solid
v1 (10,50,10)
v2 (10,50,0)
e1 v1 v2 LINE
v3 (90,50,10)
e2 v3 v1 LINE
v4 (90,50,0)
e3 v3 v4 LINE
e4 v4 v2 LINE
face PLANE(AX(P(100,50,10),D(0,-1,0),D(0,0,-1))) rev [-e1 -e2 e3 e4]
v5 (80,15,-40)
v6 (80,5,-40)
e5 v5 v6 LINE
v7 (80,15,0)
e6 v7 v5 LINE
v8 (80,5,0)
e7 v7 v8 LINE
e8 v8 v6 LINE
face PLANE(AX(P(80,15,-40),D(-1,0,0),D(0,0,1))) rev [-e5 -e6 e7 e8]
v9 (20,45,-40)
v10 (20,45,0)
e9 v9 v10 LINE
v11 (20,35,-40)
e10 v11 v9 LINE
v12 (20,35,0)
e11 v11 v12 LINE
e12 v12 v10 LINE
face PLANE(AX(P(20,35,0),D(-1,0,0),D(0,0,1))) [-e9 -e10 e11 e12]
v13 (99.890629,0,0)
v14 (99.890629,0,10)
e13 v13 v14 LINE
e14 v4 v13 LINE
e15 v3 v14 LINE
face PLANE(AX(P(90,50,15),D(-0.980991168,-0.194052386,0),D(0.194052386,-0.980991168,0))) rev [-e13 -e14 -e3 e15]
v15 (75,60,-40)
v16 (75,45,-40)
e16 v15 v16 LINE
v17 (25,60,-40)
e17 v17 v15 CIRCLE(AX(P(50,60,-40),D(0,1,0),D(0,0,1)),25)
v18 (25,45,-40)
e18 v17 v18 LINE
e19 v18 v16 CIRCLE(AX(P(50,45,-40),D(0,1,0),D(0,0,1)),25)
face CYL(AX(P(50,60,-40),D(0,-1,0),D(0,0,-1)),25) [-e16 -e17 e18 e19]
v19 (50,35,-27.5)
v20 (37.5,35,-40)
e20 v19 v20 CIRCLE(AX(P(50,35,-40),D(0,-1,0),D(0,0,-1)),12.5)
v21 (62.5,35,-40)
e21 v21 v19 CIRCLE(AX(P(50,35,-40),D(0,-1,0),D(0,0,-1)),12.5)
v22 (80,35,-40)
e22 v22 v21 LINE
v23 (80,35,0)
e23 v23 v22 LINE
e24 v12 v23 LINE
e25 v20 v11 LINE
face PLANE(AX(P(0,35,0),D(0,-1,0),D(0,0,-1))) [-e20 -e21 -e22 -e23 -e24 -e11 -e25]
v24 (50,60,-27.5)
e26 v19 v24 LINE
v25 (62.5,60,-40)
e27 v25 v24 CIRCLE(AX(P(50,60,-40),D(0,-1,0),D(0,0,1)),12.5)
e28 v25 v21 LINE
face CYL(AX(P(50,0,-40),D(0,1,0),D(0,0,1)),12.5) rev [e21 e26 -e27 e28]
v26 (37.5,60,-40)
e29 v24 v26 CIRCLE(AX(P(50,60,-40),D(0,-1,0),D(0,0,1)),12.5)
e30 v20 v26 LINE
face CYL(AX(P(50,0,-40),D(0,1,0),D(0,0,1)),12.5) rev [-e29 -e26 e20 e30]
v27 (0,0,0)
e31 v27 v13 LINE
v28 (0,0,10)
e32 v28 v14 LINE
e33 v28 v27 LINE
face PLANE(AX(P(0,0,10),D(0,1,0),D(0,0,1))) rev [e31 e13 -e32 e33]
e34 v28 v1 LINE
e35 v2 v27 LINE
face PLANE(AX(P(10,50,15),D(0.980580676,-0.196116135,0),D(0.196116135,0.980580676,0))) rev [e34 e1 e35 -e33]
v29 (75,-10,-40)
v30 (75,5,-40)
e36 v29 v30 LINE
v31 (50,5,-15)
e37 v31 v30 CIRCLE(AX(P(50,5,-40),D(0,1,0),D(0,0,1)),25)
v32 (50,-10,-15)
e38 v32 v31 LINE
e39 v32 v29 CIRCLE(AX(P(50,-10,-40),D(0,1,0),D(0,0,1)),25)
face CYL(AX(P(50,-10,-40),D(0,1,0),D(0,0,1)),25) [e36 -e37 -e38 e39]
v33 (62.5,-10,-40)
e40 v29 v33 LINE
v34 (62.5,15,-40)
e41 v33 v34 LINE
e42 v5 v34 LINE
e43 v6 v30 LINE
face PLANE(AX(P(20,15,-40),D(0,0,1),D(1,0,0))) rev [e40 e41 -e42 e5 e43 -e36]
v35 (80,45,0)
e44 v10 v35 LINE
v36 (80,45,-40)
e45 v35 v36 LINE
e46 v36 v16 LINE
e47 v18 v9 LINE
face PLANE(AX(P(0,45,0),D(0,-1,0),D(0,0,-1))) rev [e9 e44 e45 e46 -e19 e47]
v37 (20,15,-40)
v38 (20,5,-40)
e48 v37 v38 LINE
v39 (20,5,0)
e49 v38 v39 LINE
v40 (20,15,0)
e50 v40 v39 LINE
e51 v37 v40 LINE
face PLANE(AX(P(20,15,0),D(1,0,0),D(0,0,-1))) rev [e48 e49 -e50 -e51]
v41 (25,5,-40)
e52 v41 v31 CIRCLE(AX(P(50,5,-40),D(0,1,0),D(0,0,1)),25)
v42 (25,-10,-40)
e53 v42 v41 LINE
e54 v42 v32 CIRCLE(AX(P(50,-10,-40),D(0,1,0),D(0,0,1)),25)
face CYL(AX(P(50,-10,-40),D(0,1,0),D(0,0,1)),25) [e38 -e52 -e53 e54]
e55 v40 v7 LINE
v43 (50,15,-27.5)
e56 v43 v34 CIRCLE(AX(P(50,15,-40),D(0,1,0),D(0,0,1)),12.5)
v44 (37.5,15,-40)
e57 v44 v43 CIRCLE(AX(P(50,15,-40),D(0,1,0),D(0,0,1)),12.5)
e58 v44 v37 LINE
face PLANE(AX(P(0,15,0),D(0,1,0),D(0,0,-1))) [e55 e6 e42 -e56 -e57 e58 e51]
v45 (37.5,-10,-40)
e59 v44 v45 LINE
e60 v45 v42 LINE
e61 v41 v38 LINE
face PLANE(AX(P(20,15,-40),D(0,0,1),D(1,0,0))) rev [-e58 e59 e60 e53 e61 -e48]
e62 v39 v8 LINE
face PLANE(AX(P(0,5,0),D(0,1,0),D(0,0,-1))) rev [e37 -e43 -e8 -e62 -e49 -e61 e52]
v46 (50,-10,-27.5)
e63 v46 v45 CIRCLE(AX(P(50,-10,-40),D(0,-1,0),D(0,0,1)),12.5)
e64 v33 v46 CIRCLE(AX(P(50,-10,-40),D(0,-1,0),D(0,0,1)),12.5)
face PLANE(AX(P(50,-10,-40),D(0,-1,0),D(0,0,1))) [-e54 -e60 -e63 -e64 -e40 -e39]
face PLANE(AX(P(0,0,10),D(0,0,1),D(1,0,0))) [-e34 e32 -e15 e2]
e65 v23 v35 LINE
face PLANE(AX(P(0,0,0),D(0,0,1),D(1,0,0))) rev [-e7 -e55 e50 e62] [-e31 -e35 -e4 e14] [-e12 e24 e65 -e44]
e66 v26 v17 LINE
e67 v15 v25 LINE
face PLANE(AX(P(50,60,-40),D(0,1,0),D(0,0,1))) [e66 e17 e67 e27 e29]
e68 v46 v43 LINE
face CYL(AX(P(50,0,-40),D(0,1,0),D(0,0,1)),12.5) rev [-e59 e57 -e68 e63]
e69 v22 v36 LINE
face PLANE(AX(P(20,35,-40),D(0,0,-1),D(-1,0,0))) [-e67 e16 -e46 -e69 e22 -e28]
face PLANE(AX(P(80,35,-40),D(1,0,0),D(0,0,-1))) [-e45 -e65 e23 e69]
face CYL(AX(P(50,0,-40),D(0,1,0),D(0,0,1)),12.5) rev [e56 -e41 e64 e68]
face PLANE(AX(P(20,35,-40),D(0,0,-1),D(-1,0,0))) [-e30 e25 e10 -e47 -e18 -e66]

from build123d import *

# Parameters (mm, degrees)
BASE_PLATE_SKETCH_W          = 100
BASE_PLATE_SKETCH_H          = 50
BASE_PLATE_10MM_DEPTH        = 10
SUPPORT_ARM_DEPTH            = 10
ARM_RELIEF_CUT_SKETCH_R      = 12.5
ARM_RELIEF_CUT_DEPTH         = 117.726175299
BEARING_START                = 15
BEARING_SEAT_BOSS_15MM_DEPTH = 15
PLATE_TAPER_CUT_DEPTH        = 15


with BuildPart() as part:
    # Base Plate Sketch → Base Plate 10mm (new body)
    with BuildSketch(Plane.XY):
        with Locations((50, 25)):
            Rectangle(BASE_PLATE_SKETCH_W, BASE_PLATE_SKETCH_H)
    extrude(amount=BASE_PLATE_10MM_DEPTH)

    # Support Arm Sketch → Support Arm (add)
    with BuildSketch(Plane(origin=(0, 45, 0), x_dir=(1, 0, 0), z_dir=(0, 1, 0))):
        Polygon((50, 0), (20, 0), (20, 40), (80, 40), (80, 0), align=None)
    support_arm = extrude(amount=-SUPPORT_ARM_DEPTH)

    # Support Arm Mirror: Support Arm across plane
    add(support_arm.mirror(Plane.ZX.offset(25)))

    # Arm Relief Cut Sketch → Arm Relief Cut (cut, through all)
    with BuildSketch(Plane(origin=(0, 45, 0), x_dir=(1, 0, 0), z_dir=(0, 1, 0))):
        with Locations((50, 40)):
            Circle(ARM_RELIEF_CUT_SKETCH_R)
    extrude(amount=-ARM_RELIEF_CUT_DEPTH, mode=Mode.SUBTRACT)

    # Bearing Seat Boss Sketch → Bearing Seat Boss 15mm (add)
    with BuildSketch(Plane(origin=(0, 45, 0), x_dir=(1, 0, 0), z_dir=(0, 1, 0)).offset(BEARING_START)):
        with BuildLine():
            Line((25, 40), (37.5, 40))
            ThreePointArc((37.5, 40), (50, 27.5), (62.5, 40))
            Line((62.5, 40), (75, 40))
            ThreePointArc((75, 40), (50, 15), (25, 40))
        make_face()
    bearing_seat_boss_15mm = extrude(amount=-BEARING_SEAT_BOSS_15MM_DEPTH)

    # Bearing Seat Boss Mirror: Bearing Seat Boss 15mm across plane
    add(bearing_seat_boss_15mm.mirror(Plane.ZX.offset(25)))

    # Plate Taper Cut Sketch → Plate Taper Cut (cut)
    with BuildSketch(Plane(origin=(0, 0, 0), x_dir=(-1, 0, 0), z_dir=(0, 0, -1))):
        Polygon((-100, 50), (-90, 50), (-100, -0.55290415), align=None)
        Polygon((0, 50), (-10, 50), (0, 0), align=None)
    extrude(amount=-PLATE_TAPER_CUT_DEPTH, mode=Mode.SUBTRACT)


solid = part.part
